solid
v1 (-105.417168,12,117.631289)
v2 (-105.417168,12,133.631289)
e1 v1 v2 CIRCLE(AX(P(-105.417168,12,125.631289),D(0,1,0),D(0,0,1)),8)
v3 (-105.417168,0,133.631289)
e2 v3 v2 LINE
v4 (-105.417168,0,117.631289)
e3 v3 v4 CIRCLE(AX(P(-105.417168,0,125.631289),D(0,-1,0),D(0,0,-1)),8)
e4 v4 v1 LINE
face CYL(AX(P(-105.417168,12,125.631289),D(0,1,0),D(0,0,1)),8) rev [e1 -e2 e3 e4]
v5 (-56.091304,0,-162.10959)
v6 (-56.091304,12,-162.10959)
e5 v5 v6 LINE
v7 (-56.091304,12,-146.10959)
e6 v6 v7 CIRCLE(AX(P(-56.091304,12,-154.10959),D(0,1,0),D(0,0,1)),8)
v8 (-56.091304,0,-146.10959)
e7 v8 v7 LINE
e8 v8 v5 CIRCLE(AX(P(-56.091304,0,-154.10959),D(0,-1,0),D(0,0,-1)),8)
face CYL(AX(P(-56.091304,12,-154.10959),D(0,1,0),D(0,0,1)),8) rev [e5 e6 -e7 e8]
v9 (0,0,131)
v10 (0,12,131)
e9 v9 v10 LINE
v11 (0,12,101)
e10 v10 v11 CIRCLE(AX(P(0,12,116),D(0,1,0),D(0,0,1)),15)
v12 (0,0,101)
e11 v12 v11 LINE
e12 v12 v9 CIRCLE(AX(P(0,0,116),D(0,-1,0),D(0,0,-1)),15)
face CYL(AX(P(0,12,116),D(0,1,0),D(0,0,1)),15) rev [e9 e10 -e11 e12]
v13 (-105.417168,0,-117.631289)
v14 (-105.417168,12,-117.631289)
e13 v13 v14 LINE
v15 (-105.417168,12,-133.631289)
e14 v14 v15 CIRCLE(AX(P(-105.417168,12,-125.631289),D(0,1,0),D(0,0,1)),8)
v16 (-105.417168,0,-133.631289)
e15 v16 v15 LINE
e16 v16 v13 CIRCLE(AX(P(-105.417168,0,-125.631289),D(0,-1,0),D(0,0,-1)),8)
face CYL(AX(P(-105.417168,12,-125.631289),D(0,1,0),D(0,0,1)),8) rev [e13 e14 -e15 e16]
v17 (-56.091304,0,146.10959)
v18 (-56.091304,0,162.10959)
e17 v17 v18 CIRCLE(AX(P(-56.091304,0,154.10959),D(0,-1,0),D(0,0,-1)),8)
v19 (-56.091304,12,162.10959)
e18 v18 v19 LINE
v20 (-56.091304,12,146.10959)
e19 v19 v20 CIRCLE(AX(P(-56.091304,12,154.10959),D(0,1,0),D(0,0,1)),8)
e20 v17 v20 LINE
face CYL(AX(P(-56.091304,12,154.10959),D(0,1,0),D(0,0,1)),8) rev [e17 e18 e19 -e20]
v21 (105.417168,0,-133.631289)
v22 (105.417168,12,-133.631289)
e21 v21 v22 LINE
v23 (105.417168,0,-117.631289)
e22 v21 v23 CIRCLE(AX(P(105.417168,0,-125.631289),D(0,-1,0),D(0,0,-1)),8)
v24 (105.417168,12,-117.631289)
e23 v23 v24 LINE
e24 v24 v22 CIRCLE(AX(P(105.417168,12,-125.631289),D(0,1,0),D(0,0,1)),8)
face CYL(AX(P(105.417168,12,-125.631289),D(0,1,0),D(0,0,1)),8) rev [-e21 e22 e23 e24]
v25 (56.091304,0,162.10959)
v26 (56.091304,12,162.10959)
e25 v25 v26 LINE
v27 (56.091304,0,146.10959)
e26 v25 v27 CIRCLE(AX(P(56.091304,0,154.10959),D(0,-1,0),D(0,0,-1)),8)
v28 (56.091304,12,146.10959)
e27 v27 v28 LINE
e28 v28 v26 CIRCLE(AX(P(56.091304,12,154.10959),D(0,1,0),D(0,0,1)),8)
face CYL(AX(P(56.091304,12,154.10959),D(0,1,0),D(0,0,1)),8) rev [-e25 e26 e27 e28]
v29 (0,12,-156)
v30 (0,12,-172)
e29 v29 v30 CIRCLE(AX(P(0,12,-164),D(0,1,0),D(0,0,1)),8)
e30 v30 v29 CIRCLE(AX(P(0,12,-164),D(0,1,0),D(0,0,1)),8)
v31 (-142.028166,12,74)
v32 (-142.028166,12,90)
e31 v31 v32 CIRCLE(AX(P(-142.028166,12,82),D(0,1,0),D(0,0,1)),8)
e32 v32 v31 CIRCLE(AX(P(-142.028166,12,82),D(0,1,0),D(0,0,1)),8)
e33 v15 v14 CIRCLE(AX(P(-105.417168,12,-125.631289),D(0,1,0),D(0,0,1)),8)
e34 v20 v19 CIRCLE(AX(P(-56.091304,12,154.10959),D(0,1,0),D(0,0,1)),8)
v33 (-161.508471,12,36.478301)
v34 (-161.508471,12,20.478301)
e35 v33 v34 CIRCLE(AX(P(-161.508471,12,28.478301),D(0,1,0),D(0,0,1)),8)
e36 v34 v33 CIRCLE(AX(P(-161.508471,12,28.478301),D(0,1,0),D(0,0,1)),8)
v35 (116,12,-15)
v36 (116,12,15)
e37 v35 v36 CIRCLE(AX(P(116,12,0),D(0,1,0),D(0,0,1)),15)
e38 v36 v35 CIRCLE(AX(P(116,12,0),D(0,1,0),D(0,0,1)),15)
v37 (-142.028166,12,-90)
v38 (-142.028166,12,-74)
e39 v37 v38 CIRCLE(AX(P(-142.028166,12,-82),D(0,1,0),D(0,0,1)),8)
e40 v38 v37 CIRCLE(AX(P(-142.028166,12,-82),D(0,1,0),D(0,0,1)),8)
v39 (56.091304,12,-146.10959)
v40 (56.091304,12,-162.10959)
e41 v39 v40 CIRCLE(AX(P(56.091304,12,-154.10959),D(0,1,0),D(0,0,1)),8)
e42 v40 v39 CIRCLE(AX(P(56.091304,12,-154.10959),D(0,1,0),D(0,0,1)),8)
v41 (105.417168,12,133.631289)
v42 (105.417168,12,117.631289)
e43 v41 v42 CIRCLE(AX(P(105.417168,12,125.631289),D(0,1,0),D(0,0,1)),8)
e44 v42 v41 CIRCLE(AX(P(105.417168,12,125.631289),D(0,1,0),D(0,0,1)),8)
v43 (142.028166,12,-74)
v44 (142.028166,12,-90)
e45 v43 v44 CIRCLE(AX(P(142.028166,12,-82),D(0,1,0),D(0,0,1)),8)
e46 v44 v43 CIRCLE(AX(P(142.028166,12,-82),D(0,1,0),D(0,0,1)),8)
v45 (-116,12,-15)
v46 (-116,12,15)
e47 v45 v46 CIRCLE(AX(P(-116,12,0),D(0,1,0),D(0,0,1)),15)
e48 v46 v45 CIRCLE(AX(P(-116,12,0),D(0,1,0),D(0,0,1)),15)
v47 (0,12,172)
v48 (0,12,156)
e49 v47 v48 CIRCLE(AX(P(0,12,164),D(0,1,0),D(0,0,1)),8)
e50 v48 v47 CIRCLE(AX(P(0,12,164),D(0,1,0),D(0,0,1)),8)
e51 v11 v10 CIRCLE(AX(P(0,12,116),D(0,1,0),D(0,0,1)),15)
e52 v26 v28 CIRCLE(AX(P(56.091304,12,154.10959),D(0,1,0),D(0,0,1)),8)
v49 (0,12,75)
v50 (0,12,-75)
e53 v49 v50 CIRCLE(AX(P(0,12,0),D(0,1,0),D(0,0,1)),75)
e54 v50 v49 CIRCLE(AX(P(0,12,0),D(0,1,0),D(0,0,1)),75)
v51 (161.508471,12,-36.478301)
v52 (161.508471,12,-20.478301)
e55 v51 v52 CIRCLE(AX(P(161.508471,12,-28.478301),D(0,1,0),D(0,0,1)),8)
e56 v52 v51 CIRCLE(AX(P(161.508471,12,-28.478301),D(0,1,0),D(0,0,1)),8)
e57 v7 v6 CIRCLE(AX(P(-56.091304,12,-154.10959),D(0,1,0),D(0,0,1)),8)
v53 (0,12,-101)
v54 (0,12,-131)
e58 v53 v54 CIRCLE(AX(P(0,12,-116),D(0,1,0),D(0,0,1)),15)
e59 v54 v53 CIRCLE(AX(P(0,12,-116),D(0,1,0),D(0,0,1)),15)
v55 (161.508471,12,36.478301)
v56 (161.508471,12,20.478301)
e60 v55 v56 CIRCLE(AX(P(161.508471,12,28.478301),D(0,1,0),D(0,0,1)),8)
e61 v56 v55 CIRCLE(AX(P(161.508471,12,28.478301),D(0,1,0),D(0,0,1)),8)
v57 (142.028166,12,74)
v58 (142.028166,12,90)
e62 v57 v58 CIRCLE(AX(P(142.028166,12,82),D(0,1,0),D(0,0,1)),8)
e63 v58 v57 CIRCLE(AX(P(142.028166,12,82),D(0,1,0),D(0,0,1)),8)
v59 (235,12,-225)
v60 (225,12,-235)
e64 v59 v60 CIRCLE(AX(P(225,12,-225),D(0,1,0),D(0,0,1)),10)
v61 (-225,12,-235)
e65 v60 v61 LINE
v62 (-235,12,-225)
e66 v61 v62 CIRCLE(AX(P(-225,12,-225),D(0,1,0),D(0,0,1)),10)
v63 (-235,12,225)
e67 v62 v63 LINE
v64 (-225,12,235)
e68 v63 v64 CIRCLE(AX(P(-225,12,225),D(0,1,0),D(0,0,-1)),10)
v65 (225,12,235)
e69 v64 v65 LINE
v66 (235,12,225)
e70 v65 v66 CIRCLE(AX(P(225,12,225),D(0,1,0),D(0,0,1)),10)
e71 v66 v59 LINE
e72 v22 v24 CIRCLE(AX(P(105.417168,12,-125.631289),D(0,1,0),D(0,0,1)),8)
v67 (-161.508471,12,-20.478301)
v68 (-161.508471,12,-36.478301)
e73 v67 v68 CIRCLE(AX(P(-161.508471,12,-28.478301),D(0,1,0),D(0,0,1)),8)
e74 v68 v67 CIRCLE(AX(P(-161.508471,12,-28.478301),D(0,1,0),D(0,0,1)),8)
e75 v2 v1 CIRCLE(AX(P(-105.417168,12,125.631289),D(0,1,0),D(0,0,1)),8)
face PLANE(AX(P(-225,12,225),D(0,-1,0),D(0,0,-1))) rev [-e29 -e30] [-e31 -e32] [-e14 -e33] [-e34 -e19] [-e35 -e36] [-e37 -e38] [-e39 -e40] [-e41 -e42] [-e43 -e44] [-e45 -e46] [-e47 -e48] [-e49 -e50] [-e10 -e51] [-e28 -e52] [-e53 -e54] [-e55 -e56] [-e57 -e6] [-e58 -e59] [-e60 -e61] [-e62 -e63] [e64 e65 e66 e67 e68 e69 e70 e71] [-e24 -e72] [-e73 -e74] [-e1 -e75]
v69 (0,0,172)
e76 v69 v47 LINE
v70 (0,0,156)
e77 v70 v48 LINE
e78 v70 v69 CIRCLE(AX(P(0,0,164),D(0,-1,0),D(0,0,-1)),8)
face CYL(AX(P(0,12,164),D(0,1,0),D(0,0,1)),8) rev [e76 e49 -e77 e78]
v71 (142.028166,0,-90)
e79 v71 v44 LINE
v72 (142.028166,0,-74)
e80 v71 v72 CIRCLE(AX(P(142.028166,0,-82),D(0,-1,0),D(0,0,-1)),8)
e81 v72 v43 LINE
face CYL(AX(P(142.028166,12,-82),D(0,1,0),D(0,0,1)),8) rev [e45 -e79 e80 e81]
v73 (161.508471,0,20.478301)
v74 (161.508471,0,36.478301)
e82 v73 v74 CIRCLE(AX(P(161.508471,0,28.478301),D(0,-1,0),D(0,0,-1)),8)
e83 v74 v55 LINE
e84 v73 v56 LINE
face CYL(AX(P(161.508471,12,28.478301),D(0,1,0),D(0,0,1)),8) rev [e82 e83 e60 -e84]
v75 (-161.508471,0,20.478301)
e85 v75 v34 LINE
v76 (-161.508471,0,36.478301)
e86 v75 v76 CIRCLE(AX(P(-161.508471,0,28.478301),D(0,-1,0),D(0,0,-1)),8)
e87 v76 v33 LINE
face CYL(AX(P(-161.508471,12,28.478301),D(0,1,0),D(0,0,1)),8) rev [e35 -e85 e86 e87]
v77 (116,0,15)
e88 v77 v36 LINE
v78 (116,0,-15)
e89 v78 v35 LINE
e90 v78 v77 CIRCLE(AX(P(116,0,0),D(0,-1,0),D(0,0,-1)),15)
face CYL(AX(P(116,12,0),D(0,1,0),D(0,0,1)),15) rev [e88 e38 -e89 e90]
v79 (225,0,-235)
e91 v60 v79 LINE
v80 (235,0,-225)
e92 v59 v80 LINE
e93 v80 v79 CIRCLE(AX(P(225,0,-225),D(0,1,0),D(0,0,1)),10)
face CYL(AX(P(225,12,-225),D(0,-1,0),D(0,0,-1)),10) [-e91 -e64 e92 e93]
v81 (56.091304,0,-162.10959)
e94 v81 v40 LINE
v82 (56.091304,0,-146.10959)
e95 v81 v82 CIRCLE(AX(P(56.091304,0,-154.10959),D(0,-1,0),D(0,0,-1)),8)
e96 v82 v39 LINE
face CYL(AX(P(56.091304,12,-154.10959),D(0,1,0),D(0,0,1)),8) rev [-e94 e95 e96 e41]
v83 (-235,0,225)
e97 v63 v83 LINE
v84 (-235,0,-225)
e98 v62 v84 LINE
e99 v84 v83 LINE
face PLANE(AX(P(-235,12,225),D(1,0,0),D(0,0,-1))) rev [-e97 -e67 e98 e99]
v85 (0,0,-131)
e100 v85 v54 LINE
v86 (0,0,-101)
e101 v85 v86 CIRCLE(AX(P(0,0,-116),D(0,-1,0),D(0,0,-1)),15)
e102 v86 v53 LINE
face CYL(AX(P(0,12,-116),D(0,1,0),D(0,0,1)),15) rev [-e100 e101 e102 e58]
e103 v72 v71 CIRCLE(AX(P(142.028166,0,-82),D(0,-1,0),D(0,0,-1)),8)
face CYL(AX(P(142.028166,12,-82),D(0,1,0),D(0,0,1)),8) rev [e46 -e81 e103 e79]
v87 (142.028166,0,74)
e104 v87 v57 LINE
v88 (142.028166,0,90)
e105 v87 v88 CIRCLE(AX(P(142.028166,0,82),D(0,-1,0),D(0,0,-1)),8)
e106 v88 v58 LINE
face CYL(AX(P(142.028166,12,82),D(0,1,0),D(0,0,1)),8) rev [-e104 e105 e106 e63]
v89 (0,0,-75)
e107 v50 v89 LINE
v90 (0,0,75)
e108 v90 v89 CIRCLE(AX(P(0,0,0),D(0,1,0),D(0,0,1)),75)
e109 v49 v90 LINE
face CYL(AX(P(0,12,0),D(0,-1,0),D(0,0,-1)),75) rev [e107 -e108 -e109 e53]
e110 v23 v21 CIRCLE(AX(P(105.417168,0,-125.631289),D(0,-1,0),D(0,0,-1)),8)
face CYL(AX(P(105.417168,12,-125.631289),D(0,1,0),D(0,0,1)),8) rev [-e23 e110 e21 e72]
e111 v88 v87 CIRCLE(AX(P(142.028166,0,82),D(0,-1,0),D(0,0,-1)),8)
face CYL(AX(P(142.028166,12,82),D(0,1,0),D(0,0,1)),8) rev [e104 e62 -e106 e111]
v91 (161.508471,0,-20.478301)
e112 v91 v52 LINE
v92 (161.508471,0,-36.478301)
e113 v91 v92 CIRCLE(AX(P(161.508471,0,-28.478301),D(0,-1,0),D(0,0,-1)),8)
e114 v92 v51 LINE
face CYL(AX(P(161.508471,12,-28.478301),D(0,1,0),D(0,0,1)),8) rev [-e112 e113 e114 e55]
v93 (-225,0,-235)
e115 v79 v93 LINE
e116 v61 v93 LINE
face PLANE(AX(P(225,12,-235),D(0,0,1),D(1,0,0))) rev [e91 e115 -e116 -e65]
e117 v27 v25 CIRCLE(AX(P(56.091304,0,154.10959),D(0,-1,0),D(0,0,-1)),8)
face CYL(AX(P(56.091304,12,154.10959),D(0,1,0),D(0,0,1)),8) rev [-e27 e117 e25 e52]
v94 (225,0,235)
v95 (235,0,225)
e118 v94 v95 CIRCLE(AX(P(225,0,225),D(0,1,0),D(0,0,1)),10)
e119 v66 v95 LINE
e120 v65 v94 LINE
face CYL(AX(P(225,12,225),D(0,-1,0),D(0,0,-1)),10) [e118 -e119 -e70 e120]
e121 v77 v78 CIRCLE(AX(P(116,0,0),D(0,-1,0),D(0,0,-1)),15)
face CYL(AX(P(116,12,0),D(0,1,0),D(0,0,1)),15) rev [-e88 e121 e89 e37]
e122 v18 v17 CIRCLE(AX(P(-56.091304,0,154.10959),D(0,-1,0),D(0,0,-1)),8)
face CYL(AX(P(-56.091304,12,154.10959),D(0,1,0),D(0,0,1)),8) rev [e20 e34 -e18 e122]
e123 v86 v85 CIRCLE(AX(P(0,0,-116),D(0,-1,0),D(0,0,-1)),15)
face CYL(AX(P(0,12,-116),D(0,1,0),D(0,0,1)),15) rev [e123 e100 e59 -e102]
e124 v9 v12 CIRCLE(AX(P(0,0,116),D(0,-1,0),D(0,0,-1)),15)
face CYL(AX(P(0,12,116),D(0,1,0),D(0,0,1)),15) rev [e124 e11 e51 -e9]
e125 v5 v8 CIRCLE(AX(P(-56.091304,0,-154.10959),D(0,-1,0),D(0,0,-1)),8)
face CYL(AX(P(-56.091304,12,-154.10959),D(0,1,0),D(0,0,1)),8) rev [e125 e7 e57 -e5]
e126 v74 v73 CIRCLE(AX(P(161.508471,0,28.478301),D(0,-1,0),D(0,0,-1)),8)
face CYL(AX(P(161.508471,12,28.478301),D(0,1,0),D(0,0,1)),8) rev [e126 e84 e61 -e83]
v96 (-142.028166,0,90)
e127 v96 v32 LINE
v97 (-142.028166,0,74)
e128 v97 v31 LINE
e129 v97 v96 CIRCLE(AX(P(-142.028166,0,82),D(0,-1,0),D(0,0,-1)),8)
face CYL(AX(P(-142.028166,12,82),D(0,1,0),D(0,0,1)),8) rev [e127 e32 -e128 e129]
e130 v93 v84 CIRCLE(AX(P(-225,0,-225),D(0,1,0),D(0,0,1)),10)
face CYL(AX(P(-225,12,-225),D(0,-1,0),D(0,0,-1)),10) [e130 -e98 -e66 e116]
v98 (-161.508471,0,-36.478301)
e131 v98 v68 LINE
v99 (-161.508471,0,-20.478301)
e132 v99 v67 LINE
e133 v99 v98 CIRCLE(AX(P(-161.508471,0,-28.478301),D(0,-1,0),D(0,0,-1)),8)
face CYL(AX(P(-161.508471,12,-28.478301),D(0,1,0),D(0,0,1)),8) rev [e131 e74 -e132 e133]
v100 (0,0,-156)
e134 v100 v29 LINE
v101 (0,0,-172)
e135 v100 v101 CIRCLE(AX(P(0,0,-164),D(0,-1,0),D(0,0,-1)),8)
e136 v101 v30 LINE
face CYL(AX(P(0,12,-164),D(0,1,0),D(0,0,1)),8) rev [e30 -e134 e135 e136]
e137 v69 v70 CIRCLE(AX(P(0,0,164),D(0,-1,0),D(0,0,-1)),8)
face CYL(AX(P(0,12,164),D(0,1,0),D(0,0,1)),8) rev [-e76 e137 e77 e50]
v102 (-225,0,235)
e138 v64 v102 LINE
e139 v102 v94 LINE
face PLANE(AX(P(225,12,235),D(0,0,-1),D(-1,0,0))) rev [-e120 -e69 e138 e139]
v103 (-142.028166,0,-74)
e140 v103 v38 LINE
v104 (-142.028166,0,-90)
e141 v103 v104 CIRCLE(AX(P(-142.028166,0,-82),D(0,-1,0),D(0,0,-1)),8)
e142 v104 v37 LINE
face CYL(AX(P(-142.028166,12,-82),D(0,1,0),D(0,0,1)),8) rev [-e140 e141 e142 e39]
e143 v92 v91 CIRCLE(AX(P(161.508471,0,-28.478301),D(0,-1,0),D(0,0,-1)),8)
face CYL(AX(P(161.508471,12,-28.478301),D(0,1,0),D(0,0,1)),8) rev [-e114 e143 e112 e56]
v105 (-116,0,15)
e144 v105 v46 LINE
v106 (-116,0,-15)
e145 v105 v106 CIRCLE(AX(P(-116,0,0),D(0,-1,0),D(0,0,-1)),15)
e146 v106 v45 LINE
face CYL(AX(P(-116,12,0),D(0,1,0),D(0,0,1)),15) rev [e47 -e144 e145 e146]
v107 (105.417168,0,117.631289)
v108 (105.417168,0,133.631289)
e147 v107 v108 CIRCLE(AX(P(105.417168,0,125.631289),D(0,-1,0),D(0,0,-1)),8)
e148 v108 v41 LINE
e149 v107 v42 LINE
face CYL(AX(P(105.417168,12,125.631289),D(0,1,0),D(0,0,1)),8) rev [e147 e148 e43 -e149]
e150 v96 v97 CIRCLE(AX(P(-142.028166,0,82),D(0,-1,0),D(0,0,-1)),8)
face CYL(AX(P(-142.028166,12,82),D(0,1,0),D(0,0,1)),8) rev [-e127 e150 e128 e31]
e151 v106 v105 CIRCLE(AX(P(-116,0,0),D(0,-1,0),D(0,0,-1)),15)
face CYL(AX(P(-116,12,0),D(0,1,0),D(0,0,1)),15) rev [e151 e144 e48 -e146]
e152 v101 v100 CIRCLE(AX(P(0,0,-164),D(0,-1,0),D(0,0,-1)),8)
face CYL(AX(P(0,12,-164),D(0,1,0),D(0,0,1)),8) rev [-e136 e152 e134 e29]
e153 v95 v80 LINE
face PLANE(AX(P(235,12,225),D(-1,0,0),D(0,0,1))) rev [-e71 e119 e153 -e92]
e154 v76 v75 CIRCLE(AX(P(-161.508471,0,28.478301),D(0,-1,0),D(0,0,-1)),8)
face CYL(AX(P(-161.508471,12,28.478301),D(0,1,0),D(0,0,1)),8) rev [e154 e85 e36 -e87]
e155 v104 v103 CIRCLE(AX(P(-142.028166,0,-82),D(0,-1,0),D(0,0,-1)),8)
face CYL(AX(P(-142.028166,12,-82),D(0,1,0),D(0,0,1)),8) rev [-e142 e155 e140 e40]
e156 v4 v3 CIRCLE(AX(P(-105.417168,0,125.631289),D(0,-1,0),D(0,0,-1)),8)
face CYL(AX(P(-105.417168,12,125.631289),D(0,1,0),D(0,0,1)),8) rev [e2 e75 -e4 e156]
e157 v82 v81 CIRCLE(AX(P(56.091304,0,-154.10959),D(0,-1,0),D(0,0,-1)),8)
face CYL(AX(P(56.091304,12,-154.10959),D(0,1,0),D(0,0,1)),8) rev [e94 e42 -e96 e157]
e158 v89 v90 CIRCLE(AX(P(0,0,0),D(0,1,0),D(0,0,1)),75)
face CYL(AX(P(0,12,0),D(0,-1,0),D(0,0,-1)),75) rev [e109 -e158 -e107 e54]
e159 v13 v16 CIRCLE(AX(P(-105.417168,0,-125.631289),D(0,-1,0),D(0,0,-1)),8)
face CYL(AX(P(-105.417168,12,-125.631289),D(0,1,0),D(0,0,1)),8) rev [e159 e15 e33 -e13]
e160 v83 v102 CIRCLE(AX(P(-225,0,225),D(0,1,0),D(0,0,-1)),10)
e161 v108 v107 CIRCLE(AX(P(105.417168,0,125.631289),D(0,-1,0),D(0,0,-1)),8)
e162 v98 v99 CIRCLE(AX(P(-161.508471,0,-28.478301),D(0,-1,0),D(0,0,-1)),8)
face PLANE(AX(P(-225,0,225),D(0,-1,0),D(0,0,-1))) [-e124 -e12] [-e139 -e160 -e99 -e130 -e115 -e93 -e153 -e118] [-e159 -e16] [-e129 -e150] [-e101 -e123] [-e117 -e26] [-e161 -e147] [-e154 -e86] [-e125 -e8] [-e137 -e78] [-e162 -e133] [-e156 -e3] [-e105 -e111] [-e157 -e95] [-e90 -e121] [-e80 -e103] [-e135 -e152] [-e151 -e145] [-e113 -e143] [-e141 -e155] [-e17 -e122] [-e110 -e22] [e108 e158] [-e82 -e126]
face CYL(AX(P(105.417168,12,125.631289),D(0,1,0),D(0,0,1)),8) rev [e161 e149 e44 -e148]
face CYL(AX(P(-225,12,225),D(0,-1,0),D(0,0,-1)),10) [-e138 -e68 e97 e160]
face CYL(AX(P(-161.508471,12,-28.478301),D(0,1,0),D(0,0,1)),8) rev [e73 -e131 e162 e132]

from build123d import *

# Parameters (mm, degrees)
SKETCH1_R                  = 75
BOSS_EXTRUDE1_DEPTH        = 12
F_16_0_16_DIAMETER_HOLE1_D = 16
F_30_DIAMETER_HOLE2_D      = 30


with BuildPart() as part:
    # Sketch1 → Boss-Extrude1 (new body)
    with BuildSketch(Plane(origin=(0, 0, 0), x_dir=(1, 0, 0), z_dir=(0, 1, 0))):
        with BuildLine():
            Line((225, -235), (-225, -235))
            ThreePointArc((-225, -235), (-232.071067812, -232.071067812), (-235, -225))
            Line((-235, -225), (-235, 225))
            ThreePointArc((-235, 225), (-232.071067812, 232.071067812), (-225, 235))
            Line((-225, 235), (225, 235))
            ThreePointArc((225, 235), (232.071067812, 232.071067812), (235, 225))
            Line((235, 225), (235, -225))
            ThreePointArc((235, -225), (232.071067812, -232.071067812), (225, -235))
        make_face()
        with Locations(Location((0, 0, 0), (0, 0, 270))):
            Circle(SKETCH1_R, mode=Mode.SUBTRACT)
    extrude(amount=BOSS_EXTRUDE1_DEPTH)

    # Ø16.0 (16) Diameter Hole1 (through all)
    with Locations(Plane(origin=(0, 12, 0), x_dir=(1, 0, 0), z_dir=(0, 1, 0))):
        with Locations((0, 164), (56.091303505, 154.109589809), (105.417167989, 125.631288672), (142.028166221, 82), (161.508471494, 28.478301137), (161.508471494, -28.478301137), (142.028166221, -82), (105.417167989, -125.631288672), (56.091303505, -154.109589809), (0, -164), (-56.091303505, -154.109589809), (-105.417167989, -125.631288672), (-142.028166221, -82), (-161.508471494, -28.478301137), (-161.508471494, 28.478301137), (-142.028166221, 82), (-105.417167989, 125.631288672), (-56.091303505, 154.109589809)):
            Hole(F_16_0_16_DIAMETER_HOLE1_D / 2)

    # Ø30 Diameter Hole2 (through all)
    with Locations(Plane(origin=(0, 12, 0), x_dir=(1, 0, 0), z_dir=(0, 1, 0))):
        with Locations((0, 116), (116, 0), (0, -116), (-116, 0)):
            Hole(F_30_DIAMETER_HOLE2_D / 2)


solid = part.part
